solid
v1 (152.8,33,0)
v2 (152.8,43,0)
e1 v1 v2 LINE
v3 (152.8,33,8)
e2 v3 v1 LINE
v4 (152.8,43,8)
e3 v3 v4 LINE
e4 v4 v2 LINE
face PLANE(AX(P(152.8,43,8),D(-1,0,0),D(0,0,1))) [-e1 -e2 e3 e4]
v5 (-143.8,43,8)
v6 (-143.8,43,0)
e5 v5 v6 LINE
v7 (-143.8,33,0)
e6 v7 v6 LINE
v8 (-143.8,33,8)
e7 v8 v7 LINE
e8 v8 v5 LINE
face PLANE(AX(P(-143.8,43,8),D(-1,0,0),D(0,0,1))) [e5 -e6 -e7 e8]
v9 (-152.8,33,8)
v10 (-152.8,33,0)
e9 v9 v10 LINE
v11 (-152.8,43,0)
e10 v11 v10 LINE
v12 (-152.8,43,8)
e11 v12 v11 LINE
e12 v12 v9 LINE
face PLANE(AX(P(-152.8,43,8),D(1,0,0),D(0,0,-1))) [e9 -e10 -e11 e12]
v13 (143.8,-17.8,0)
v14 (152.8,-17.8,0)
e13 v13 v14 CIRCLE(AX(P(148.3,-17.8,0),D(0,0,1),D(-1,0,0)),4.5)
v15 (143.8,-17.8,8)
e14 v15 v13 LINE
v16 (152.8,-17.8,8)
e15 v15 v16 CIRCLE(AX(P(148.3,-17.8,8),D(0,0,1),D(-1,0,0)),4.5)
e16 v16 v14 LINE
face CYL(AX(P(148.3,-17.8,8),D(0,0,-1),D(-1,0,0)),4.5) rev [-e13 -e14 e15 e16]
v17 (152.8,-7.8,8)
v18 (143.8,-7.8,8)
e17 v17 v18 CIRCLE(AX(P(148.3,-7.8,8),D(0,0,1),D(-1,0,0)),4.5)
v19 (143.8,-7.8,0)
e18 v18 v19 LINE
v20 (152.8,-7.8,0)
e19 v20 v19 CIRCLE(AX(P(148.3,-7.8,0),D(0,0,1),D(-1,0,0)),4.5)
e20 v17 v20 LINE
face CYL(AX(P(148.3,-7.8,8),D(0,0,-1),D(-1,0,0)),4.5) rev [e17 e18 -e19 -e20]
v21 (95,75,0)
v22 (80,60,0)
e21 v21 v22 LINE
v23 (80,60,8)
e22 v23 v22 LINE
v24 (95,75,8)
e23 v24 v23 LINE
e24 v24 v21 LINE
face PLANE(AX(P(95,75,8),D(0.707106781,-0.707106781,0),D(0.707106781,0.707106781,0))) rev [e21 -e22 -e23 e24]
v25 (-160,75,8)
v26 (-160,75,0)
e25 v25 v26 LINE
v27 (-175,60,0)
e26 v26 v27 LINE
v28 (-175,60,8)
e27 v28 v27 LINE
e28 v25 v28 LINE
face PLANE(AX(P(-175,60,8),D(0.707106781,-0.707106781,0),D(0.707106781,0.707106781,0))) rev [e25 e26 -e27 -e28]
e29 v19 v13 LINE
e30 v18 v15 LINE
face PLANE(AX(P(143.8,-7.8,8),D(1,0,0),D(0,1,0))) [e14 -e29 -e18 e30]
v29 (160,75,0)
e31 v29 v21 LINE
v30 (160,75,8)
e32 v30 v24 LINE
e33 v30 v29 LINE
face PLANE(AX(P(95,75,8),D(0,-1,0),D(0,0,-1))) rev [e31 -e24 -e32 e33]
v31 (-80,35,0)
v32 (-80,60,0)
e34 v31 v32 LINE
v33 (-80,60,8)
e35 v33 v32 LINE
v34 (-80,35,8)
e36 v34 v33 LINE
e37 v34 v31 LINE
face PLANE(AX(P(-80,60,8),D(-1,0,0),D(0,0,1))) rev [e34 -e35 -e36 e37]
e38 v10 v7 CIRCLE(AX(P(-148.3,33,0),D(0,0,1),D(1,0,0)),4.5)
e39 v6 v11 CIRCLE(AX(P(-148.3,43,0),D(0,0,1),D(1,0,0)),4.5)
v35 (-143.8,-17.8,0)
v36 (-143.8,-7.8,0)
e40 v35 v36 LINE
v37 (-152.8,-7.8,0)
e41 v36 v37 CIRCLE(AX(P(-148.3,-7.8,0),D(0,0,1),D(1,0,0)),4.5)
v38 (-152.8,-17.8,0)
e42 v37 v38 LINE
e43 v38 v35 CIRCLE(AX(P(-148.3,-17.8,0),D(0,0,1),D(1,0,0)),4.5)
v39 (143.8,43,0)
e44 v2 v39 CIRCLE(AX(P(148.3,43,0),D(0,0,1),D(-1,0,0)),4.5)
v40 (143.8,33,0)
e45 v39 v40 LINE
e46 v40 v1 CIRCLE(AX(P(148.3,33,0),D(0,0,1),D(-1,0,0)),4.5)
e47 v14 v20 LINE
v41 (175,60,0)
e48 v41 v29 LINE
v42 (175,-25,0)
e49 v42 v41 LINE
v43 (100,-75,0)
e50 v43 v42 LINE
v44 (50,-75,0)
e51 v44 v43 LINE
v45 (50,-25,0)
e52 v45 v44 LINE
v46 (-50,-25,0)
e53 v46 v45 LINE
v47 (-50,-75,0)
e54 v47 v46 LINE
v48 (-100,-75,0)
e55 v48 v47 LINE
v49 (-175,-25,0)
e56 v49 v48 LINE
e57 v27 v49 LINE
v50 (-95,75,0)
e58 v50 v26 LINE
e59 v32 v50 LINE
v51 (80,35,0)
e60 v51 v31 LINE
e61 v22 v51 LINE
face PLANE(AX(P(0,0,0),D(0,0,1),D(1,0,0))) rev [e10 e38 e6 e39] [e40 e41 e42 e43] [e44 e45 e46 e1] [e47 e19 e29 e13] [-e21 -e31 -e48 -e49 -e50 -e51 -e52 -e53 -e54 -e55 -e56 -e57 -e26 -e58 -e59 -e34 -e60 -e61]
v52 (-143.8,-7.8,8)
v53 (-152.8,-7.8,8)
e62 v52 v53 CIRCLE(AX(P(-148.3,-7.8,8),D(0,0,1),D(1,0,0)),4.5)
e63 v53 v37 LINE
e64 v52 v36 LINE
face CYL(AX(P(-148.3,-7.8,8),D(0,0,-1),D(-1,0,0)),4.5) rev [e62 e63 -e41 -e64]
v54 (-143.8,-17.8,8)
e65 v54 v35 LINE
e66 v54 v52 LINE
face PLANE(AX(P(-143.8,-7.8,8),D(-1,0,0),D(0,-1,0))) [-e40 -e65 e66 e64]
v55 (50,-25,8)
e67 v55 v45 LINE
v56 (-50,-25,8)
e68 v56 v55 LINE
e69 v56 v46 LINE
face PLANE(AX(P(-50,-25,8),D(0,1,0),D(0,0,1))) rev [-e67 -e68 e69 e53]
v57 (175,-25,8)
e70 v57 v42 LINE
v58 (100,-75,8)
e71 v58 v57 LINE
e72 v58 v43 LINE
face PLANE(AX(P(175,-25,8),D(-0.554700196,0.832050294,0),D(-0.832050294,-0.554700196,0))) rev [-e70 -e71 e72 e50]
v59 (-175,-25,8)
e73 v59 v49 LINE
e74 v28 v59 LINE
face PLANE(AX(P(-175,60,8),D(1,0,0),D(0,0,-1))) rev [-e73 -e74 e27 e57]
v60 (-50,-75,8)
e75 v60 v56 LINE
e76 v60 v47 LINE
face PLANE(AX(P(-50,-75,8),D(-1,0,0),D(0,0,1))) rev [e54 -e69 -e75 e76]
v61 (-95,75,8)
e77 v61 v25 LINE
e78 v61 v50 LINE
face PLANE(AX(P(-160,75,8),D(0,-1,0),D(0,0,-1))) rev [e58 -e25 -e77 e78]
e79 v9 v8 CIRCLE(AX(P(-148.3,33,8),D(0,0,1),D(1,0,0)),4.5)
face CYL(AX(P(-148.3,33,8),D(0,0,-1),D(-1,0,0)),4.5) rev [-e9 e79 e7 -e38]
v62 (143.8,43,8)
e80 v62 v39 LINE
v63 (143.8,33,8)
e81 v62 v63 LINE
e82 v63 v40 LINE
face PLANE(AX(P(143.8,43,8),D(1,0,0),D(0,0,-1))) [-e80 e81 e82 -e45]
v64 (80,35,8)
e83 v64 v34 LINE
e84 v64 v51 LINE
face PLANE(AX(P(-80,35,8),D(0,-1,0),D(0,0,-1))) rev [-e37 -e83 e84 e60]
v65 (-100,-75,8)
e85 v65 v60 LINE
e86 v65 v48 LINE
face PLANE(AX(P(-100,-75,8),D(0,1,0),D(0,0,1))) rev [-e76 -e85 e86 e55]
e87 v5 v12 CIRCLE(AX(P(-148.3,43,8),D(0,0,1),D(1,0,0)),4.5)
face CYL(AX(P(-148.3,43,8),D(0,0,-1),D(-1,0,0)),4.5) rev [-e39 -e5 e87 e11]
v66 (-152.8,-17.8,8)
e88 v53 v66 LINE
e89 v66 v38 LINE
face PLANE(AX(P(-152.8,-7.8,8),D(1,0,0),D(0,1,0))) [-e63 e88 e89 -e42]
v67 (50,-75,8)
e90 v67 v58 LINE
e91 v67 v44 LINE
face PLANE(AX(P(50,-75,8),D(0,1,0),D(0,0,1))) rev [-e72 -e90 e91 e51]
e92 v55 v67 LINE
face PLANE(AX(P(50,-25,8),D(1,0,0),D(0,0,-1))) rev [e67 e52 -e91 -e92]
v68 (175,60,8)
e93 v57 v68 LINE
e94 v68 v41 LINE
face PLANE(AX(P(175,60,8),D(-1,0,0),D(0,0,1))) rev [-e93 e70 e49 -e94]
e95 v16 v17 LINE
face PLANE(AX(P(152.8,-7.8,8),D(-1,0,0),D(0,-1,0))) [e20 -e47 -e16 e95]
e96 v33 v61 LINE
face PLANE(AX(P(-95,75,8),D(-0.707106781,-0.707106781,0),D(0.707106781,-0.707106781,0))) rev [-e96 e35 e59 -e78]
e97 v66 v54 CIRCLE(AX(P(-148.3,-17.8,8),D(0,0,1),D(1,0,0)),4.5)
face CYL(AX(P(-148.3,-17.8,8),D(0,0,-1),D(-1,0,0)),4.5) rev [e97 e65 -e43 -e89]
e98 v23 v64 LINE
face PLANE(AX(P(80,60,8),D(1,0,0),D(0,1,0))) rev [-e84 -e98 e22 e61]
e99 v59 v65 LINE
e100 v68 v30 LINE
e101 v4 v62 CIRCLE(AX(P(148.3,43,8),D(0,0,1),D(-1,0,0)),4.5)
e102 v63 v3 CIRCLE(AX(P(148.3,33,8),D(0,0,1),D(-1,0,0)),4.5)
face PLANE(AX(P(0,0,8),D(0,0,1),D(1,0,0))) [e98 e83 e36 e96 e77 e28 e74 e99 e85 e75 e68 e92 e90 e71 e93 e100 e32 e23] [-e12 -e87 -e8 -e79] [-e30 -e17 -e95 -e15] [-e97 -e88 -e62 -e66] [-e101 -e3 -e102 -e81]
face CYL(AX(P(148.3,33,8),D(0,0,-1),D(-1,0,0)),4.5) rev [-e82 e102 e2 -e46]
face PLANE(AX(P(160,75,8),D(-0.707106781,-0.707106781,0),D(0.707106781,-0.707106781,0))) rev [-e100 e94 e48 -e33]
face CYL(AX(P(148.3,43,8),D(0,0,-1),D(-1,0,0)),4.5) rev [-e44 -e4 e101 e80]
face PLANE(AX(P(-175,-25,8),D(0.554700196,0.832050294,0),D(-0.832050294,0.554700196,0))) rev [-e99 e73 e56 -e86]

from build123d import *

# Parameters (mm, degrees)
EXTRUDE_1_DEPTH = 8


with BuildPart() as part:
    # 草图1 → 凸台-拉伸1 (new body)
    with BuildSketch(Plane.XY):
        Polygon((175, -25), (100, -75), (50, -75), (50, -25), (-50, -25), (-50, -75), (-100, -75), (-175, -25), (-175, 60), (-160, 75), (-95, 75), (-80, 60), (-80, 35), (80, 35), (80, 60), (95, 75), (160, 75), (175, 60), align=None)
        with BuildLine():
            Line((-143.8, 43), (-143.8, 33))
            ThreePointArc((-143.8, 33), (-148.3, 28.5), (-152.8, 33))
            Line((-152.8, 33), (-152.8, 43))
            ThreePointArc((-152.8, 43), (-148.3, 47.5), (-143.8, 43))
        make_face(mode=Mode.SUBTRACT)
        with BuildLine():
            Line((-143.8, -7.8), (-143.8, -17.8))
            ThreePointArc((-143.8, -17.8), (-148.3, -22.3), (-152.8, -17.8))
            Line((-152.8, -17.8), (-152.8, -7.8))
            ThreePointArc((-152.8, -7.8), (-148.3, -3.3), (-143.8, -7.8))
        make_face(mode=Mode.SUBTRACT)
        with BuildLine():
            Line((143.8, -7.8), (143.8, -17.8))
            ThreePointArc((143.8, -17.8), (148.3, -22.3), (152.8, -17.8))
            Line((152.8, -17.8), (152.8, -7.8))
            ThreePointArc((152.8, -7.8), (148.3, -3.3), (143.8, -7.8))
        make_face(mode=Mode.SUBTRACT)
        with BuildLine():
            Line((143.8, 43), (143.8, 33))
            ThreePointArc((143.8, 33), (148.3, 28.5), (152.8, 33))
            Line((152.8, 33), (152.8, 43))
            ThreePointArc((152.8, 43), (148.3, 47.5), (143.8, 43))
        make_face(mode=Mode.SUBTRACT)
    extrude(amount=EXTRUDE_1_DEPTH)


solid = part.part
